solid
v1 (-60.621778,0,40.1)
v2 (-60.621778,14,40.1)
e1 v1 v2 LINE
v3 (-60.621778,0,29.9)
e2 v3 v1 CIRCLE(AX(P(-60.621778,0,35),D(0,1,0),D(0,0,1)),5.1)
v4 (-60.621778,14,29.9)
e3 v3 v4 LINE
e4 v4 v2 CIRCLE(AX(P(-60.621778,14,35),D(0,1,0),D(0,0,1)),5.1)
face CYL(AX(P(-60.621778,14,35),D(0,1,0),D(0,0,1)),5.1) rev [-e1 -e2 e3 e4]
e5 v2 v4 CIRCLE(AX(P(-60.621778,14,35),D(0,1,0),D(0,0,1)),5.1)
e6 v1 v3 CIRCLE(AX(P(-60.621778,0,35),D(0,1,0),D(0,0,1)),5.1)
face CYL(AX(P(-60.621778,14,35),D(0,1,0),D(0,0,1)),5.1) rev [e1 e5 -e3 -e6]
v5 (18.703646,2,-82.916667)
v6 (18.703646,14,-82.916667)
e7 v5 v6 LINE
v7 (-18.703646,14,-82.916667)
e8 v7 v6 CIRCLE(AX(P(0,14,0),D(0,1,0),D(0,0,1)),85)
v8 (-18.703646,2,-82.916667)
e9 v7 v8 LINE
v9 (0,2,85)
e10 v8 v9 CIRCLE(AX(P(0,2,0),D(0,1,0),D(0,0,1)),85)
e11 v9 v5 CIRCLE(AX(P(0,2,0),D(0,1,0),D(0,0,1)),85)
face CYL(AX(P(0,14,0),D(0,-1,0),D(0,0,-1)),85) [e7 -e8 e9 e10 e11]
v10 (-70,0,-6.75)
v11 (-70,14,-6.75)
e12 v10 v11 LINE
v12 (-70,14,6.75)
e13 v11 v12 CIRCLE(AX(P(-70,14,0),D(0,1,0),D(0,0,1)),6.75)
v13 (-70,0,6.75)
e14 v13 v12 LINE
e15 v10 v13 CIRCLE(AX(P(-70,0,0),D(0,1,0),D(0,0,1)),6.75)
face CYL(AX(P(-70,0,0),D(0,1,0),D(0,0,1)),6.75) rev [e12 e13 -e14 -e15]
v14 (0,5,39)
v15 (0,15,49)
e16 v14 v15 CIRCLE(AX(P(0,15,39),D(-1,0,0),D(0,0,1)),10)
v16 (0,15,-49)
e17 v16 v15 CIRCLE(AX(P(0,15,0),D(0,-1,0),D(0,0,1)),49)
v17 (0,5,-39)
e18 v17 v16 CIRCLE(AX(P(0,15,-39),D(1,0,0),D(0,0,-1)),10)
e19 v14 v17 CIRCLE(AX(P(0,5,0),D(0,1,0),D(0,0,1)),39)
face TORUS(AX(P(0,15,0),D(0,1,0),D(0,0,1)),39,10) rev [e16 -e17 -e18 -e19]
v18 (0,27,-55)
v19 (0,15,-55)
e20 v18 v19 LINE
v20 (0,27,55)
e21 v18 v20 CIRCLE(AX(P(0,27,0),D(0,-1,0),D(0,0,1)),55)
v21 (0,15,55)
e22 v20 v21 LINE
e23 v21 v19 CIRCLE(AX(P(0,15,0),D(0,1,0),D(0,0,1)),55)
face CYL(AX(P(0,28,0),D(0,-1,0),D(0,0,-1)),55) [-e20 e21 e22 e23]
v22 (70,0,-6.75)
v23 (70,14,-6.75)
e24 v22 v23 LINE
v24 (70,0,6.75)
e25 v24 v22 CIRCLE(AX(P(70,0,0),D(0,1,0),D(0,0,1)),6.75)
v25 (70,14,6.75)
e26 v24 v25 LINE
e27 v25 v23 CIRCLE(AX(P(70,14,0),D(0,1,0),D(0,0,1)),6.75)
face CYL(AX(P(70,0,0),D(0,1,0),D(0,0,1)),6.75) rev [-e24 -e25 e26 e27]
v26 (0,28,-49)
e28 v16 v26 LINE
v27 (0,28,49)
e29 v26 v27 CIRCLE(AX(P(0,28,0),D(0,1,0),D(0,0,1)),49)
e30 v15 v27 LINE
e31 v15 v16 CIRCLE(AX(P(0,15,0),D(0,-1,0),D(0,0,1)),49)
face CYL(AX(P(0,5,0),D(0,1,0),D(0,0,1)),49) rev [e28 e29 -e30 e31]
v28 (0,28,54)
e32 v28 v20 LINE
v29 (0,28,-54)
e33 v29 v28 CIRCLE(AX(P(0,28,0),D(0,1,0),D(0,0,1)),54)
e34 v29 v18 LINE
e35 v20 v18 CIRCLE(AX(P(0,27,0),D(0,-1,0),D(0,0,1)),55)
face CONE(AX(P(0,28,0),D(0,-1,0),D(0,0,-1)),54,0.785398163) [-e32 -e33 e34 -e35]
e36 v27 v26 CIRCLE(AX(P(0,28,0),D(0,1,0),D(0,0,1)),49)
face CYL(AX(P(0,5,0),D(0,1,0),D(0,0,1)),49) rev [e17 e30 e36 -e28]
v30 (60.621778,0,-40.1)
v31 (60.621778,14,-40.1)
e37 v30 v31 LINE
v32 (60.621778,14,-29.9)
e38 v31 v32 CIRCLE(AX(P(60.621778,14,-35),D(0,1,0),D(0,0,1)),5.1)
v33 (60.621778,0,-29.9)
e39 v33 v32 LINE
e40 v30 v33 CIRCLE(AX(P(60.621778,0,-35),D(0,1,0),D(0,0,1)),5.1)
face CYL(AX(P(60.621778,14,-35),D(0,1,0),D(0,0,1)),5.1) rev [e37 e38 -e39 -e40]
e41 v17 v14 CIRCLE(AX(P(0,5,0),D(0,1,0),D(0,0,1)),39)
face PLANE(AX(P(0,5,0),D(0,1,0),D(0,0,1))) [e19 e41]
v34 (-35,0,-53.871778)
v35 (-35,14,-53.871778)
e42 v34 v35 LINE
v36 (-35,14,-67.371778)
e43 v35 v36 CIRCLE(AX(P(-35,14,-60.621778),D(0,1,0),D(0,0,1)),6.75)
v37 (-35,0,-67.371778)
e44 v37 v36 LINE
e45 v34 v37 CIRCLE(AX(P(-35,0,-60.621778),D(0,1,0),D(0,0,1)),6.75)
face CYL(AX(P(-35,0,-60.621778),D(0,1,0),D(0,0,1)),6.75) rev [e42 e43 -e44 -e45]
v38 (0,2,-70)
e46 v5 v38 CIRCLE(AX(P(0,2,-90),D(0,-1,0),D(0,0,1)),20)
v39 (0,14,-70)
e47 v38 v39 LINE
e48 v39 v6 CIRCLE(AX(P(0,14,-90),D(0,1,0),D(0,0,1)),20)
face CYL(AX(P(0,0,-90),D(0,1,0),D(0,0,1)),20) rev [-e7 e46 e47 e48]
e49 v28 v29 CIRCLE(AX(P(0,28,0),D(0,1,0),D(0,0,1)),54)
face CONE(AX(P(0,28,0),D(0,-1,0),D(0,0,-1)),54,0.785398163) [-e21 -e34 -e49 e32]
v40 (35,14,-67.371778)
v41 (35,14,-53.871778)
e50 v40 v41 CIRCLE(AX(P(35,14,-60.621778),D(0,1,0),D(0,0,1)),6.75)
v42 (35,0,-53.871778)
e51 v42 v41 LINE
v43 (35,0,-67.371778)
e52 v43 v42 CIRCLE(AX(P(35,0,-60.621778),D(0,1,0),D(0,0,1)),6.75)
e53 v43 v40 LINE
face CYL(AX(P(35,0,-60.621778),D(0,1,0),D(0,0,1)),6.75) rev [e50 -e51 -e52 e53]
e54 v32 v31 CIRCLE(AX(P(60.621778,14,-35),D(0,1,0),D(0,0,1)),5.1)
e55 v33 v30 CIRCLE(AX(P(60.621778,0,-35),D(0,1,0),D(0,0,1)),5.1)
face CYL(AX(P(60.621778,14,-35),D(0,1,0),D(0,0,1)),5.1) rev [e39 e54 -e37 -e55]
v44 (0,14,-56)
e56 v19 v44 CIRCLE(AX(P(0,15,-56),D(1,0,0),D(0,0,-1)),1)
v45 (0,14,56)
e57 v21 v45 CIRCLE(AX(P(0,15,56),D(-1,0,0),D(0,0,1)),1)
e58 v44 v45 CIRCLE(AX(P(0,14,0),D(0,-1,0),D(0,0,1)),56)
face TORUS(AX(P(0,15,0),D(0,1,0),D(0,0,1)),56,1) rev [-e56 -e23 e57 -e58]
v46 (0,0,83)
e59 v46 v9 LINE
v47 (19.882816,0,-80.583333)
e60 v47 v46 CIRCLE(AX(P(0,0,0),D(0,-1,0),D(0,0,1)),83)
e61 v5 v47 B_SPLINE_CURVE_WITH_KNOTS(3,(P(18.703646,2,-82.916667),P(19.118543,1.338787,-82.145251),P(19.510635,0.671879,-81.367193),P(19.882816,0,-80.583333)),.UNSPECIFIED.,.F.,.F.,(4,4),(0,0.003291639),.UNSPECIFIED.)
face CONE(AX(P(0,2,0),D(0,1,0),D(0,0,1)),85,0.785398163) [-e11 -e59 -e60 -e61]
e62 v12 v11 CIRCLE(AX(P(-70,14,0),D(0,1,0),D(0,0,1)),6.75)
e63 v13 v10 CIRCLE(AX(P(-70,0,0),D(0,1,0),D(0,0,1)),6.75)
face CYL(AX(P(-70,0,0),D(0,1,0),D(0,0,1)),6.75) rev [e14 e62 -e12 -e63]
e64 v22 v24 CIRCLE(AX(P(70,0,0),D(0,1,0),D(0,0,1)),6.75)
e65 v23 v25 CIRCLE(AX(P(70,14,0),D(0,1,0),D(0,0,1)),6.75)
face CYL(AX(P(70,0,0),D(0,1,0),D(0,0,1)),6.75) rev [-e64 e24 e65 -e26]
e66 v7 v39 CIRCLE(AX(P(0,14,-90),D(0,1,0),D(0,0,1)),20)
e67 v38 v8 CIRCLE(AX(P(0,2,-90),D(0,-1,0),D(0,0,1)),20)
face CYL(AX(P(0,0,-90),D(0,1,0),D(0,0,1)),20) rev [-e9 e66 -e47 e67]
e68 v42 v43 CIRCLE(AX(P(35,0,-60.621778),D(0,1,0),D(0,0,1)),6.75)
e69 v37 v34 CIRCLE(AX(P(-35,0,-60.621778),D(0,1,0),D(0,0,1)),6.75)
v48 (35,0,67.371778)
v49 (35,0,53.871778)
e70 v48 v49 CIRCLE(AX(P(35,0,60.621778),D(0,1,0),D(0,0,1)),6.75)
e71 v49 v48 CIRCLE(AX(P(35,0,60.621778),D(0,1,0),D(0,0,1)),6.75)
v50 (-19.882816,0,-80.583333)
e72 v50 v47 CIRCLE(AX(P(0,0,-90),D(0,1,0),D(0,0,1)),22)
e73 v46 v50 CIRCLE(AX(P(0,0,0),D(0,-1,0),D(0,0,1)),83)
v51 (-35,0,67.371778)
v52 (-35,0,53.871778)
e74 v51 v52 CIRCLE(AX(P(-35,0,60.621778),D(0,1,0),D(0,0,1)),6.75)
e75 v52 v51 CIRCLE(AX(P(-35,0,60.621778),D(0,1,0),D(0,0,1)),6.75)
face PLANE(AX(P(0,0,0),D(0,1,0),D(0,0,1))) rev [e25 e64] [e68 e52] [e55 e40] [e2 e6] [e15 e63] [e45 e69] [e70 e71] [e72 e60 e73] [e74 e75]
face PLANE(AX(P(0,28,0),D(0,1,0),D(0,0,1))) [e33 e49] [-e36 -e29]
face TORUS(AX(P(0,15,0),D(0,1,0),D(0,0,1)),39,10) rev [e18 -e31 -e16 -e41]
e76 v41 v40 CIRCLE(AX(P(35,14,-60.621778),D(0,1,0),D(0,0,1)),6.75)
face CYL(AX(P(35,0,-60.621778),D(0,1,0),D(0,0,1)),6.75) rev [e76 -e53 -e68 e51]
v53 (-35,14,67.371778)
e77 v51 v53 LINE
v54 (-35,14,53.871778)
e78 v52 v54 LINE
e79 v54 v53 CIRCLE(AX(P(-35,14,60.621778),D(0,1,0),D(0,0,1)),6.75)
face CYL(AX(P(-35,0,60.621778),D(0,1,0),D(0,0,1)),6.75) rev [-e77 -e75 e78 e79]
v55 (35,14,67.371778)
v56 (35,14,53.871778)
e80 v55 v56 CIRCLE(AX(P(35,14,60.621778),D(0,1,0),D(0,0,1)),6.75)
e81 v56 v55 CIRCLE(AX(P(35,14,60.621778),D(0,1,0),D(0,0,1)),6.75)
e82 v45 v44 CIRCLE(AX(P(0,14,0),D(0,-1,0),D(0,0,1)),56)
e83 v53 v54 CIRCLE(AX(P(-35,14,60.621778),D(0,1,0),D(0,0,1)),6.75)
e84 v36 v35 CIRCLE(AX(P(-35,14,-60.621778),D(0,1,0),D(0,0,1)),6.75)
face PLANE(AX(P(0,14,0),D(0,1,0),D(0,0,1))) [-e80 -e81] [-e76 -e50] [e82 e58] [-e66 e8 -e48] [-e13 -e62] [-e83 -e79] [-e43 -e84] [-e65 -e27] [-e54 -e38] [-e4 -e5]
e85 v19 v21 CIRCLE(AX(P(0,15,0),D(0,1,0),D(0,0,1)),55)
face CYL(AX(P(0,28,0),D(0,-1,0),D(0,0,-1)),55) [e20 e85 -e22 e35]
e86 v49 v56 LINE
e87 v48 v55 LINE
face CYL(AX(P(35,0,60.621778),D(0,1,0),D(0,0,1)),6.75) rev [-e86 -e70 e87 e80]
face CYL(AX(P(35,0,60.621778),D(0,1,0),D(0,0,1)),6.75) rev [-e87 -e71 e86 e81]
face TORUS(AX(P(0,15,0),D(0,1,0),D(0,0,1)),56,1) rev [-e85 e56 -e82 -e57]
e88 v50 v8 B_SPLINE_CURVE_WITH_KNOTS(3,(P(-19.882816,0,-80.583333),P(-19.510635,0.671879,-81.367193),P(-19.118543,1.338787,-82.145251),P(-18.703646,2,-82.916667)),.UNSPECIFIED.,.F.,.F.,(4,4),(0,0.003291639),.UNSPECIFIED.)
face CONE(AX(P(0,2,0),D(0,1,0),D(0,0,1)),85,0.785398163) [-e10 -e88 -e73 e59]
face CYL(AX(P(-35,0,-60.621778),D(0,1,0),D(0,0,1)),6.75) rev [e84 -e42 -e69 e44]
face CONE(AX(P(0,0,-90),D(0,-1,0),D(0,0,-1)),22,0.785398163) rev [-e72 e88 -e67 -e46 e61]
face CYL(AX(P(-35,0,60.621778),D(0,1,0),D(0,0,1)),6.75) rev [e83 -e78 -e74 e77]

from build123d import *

# Parameters (mm, degrees)
SKETCH1_R           = 85
BOSS_EXTRUDE1_DEPTH = 14
SKETCH2_R           = 55
BOSS_EXTRUDE2_DEPTH = 14
SKETCH3_R           = 49
CUT_EXTRUDE1_DEPTH  = 23
FILLET1_R           = 10
FILLET2_R           = 1
CHAMFER1_SIZE       = 1
SKETCH4_R           = 20
SKETCH4_R_2         = 6.75
CUT_EXTRUDE2_DEPTH  = 122.020659393
M12_TAPPED_HOLE1_D  = 10.2
CHAMFER2_SIZE       = 2


with BuildPart() as part:
    # Sketch1 → Boss-Extrude1 (new body)
    with BuildSketch(Plane(origin=(0, 0, 0), x_dir=(1, 0, 0), z_dir=(0, 1, 0))):
        with Locations(Location((0, 0, 0), (0, 0, 270))):
            Circle(SKETCH1_R)
    extrude(amount=BOSS_EXTRUDE1_DEPTH)

    # Sketch2 → Boss-Extrude2 (add)
    with BuildSketch(Plane(origin=(0, 14, 0), x_dir=(1, 0, 0), z_dir=(0, 1, 0))):
        with Locations(Location((0, 0, 0), (0, 0, 270))):
            Circle(SKETCH2_R)
    extrude(amount=BOSS_EXTRUDE2_DEPTH)

    # Sketch3 → Cut-Extrude1 (cut)
    with BuildSketch(Plane(origin=(0, 28, 0), x_dir=(1, 0, 0), z_dir=(0, 1, 0))):
        with Locations(Location((0, 0, 0), (0, 0, 270))):
            Circle(SKETCH3_R)
    extrude(amount=-CUT_EXTRUDE1_DEPTH, mode=Mode.SUBTRACT)

    # Fillet1
    fillet1_edges = [part.edges().sort_by_distance(p)[0] for p in [
        (0, 5, -49),
    ]]
    fillet(fillet1_edges, radius=FILLET1_R)

    # Fillet2
    fillet2_edges = [part.edges().sort_by_distance(p)[0] for p in [
        (0, 14, -55),
    ]]
    fillet(fillet2_edges, radius=FILLET2_R)

    # Chamfer1
    chamfer1_edges = [part.edges().sort_by_distance(p)[0] for p in [
        (0, 28, -55),
    ]]
    chamfer(chamfer1_edges, length=CHAMFER1_SIZE)

    # Sketch4 → Cut-Extrude2 (cut, through all)
    with BuildSketch(Plane(origin=(0, 14, 0), x_dir=(1, 0, 0), z_dir=(0, 1, 0))):
        with Locations((0, 90)):
            Circle(SKETCH4_R)
        with Locations(Location((-35, 60.621778265, 0), (0, 0, 270))):
            Circle(SKETCH4_R_2)
        with Locations(Location((35, 60.621778265, 0), (0, 0, 270))):
            Circle(SKETCH4_R_2)
        with Locations(Location((70, 0, 0), (0, 0, 270))):
            Circle(SKETCH4_R_2)
        with Locations(Location((35, -60.621778265, 0), (0, 0, 270))):
            Circle(SKETCH4_R_2)
        with Locations(Location((-35, -60.621778265, 0), (0, 0, 270))):
            Circle(SKETCH4_R_2)
        with Locations(Location((-70, 0, 0), (0, 0, 270))):
            Circle(SKETCH4_R_2)
    extrude(amount=-CUT_EXTRUDE2_DEPTH, mode=Mode.SUBTRACT)

    # M12 Tapped Hole1 (through all)
    with Locations(Plane(origin=(0, 14, 0), x_dir=(1, 0, 0), z_dir=(0, 1, 0))):
        with Locations((-60.621778265, -35), (60.621778265, 35)):
            Hole(M12_TAPPED_HOLE1_D / 2)

    # Chamfer2
    chamfer2_edges = [part.edges().sort_by_distance(p)[0] for p in [
        (0, 0, 85),
        (0, 0, -70),
    ]]
    chamfer(chamfer2_edges, length=CHAMFER2_SIZE)


solid = part.part
